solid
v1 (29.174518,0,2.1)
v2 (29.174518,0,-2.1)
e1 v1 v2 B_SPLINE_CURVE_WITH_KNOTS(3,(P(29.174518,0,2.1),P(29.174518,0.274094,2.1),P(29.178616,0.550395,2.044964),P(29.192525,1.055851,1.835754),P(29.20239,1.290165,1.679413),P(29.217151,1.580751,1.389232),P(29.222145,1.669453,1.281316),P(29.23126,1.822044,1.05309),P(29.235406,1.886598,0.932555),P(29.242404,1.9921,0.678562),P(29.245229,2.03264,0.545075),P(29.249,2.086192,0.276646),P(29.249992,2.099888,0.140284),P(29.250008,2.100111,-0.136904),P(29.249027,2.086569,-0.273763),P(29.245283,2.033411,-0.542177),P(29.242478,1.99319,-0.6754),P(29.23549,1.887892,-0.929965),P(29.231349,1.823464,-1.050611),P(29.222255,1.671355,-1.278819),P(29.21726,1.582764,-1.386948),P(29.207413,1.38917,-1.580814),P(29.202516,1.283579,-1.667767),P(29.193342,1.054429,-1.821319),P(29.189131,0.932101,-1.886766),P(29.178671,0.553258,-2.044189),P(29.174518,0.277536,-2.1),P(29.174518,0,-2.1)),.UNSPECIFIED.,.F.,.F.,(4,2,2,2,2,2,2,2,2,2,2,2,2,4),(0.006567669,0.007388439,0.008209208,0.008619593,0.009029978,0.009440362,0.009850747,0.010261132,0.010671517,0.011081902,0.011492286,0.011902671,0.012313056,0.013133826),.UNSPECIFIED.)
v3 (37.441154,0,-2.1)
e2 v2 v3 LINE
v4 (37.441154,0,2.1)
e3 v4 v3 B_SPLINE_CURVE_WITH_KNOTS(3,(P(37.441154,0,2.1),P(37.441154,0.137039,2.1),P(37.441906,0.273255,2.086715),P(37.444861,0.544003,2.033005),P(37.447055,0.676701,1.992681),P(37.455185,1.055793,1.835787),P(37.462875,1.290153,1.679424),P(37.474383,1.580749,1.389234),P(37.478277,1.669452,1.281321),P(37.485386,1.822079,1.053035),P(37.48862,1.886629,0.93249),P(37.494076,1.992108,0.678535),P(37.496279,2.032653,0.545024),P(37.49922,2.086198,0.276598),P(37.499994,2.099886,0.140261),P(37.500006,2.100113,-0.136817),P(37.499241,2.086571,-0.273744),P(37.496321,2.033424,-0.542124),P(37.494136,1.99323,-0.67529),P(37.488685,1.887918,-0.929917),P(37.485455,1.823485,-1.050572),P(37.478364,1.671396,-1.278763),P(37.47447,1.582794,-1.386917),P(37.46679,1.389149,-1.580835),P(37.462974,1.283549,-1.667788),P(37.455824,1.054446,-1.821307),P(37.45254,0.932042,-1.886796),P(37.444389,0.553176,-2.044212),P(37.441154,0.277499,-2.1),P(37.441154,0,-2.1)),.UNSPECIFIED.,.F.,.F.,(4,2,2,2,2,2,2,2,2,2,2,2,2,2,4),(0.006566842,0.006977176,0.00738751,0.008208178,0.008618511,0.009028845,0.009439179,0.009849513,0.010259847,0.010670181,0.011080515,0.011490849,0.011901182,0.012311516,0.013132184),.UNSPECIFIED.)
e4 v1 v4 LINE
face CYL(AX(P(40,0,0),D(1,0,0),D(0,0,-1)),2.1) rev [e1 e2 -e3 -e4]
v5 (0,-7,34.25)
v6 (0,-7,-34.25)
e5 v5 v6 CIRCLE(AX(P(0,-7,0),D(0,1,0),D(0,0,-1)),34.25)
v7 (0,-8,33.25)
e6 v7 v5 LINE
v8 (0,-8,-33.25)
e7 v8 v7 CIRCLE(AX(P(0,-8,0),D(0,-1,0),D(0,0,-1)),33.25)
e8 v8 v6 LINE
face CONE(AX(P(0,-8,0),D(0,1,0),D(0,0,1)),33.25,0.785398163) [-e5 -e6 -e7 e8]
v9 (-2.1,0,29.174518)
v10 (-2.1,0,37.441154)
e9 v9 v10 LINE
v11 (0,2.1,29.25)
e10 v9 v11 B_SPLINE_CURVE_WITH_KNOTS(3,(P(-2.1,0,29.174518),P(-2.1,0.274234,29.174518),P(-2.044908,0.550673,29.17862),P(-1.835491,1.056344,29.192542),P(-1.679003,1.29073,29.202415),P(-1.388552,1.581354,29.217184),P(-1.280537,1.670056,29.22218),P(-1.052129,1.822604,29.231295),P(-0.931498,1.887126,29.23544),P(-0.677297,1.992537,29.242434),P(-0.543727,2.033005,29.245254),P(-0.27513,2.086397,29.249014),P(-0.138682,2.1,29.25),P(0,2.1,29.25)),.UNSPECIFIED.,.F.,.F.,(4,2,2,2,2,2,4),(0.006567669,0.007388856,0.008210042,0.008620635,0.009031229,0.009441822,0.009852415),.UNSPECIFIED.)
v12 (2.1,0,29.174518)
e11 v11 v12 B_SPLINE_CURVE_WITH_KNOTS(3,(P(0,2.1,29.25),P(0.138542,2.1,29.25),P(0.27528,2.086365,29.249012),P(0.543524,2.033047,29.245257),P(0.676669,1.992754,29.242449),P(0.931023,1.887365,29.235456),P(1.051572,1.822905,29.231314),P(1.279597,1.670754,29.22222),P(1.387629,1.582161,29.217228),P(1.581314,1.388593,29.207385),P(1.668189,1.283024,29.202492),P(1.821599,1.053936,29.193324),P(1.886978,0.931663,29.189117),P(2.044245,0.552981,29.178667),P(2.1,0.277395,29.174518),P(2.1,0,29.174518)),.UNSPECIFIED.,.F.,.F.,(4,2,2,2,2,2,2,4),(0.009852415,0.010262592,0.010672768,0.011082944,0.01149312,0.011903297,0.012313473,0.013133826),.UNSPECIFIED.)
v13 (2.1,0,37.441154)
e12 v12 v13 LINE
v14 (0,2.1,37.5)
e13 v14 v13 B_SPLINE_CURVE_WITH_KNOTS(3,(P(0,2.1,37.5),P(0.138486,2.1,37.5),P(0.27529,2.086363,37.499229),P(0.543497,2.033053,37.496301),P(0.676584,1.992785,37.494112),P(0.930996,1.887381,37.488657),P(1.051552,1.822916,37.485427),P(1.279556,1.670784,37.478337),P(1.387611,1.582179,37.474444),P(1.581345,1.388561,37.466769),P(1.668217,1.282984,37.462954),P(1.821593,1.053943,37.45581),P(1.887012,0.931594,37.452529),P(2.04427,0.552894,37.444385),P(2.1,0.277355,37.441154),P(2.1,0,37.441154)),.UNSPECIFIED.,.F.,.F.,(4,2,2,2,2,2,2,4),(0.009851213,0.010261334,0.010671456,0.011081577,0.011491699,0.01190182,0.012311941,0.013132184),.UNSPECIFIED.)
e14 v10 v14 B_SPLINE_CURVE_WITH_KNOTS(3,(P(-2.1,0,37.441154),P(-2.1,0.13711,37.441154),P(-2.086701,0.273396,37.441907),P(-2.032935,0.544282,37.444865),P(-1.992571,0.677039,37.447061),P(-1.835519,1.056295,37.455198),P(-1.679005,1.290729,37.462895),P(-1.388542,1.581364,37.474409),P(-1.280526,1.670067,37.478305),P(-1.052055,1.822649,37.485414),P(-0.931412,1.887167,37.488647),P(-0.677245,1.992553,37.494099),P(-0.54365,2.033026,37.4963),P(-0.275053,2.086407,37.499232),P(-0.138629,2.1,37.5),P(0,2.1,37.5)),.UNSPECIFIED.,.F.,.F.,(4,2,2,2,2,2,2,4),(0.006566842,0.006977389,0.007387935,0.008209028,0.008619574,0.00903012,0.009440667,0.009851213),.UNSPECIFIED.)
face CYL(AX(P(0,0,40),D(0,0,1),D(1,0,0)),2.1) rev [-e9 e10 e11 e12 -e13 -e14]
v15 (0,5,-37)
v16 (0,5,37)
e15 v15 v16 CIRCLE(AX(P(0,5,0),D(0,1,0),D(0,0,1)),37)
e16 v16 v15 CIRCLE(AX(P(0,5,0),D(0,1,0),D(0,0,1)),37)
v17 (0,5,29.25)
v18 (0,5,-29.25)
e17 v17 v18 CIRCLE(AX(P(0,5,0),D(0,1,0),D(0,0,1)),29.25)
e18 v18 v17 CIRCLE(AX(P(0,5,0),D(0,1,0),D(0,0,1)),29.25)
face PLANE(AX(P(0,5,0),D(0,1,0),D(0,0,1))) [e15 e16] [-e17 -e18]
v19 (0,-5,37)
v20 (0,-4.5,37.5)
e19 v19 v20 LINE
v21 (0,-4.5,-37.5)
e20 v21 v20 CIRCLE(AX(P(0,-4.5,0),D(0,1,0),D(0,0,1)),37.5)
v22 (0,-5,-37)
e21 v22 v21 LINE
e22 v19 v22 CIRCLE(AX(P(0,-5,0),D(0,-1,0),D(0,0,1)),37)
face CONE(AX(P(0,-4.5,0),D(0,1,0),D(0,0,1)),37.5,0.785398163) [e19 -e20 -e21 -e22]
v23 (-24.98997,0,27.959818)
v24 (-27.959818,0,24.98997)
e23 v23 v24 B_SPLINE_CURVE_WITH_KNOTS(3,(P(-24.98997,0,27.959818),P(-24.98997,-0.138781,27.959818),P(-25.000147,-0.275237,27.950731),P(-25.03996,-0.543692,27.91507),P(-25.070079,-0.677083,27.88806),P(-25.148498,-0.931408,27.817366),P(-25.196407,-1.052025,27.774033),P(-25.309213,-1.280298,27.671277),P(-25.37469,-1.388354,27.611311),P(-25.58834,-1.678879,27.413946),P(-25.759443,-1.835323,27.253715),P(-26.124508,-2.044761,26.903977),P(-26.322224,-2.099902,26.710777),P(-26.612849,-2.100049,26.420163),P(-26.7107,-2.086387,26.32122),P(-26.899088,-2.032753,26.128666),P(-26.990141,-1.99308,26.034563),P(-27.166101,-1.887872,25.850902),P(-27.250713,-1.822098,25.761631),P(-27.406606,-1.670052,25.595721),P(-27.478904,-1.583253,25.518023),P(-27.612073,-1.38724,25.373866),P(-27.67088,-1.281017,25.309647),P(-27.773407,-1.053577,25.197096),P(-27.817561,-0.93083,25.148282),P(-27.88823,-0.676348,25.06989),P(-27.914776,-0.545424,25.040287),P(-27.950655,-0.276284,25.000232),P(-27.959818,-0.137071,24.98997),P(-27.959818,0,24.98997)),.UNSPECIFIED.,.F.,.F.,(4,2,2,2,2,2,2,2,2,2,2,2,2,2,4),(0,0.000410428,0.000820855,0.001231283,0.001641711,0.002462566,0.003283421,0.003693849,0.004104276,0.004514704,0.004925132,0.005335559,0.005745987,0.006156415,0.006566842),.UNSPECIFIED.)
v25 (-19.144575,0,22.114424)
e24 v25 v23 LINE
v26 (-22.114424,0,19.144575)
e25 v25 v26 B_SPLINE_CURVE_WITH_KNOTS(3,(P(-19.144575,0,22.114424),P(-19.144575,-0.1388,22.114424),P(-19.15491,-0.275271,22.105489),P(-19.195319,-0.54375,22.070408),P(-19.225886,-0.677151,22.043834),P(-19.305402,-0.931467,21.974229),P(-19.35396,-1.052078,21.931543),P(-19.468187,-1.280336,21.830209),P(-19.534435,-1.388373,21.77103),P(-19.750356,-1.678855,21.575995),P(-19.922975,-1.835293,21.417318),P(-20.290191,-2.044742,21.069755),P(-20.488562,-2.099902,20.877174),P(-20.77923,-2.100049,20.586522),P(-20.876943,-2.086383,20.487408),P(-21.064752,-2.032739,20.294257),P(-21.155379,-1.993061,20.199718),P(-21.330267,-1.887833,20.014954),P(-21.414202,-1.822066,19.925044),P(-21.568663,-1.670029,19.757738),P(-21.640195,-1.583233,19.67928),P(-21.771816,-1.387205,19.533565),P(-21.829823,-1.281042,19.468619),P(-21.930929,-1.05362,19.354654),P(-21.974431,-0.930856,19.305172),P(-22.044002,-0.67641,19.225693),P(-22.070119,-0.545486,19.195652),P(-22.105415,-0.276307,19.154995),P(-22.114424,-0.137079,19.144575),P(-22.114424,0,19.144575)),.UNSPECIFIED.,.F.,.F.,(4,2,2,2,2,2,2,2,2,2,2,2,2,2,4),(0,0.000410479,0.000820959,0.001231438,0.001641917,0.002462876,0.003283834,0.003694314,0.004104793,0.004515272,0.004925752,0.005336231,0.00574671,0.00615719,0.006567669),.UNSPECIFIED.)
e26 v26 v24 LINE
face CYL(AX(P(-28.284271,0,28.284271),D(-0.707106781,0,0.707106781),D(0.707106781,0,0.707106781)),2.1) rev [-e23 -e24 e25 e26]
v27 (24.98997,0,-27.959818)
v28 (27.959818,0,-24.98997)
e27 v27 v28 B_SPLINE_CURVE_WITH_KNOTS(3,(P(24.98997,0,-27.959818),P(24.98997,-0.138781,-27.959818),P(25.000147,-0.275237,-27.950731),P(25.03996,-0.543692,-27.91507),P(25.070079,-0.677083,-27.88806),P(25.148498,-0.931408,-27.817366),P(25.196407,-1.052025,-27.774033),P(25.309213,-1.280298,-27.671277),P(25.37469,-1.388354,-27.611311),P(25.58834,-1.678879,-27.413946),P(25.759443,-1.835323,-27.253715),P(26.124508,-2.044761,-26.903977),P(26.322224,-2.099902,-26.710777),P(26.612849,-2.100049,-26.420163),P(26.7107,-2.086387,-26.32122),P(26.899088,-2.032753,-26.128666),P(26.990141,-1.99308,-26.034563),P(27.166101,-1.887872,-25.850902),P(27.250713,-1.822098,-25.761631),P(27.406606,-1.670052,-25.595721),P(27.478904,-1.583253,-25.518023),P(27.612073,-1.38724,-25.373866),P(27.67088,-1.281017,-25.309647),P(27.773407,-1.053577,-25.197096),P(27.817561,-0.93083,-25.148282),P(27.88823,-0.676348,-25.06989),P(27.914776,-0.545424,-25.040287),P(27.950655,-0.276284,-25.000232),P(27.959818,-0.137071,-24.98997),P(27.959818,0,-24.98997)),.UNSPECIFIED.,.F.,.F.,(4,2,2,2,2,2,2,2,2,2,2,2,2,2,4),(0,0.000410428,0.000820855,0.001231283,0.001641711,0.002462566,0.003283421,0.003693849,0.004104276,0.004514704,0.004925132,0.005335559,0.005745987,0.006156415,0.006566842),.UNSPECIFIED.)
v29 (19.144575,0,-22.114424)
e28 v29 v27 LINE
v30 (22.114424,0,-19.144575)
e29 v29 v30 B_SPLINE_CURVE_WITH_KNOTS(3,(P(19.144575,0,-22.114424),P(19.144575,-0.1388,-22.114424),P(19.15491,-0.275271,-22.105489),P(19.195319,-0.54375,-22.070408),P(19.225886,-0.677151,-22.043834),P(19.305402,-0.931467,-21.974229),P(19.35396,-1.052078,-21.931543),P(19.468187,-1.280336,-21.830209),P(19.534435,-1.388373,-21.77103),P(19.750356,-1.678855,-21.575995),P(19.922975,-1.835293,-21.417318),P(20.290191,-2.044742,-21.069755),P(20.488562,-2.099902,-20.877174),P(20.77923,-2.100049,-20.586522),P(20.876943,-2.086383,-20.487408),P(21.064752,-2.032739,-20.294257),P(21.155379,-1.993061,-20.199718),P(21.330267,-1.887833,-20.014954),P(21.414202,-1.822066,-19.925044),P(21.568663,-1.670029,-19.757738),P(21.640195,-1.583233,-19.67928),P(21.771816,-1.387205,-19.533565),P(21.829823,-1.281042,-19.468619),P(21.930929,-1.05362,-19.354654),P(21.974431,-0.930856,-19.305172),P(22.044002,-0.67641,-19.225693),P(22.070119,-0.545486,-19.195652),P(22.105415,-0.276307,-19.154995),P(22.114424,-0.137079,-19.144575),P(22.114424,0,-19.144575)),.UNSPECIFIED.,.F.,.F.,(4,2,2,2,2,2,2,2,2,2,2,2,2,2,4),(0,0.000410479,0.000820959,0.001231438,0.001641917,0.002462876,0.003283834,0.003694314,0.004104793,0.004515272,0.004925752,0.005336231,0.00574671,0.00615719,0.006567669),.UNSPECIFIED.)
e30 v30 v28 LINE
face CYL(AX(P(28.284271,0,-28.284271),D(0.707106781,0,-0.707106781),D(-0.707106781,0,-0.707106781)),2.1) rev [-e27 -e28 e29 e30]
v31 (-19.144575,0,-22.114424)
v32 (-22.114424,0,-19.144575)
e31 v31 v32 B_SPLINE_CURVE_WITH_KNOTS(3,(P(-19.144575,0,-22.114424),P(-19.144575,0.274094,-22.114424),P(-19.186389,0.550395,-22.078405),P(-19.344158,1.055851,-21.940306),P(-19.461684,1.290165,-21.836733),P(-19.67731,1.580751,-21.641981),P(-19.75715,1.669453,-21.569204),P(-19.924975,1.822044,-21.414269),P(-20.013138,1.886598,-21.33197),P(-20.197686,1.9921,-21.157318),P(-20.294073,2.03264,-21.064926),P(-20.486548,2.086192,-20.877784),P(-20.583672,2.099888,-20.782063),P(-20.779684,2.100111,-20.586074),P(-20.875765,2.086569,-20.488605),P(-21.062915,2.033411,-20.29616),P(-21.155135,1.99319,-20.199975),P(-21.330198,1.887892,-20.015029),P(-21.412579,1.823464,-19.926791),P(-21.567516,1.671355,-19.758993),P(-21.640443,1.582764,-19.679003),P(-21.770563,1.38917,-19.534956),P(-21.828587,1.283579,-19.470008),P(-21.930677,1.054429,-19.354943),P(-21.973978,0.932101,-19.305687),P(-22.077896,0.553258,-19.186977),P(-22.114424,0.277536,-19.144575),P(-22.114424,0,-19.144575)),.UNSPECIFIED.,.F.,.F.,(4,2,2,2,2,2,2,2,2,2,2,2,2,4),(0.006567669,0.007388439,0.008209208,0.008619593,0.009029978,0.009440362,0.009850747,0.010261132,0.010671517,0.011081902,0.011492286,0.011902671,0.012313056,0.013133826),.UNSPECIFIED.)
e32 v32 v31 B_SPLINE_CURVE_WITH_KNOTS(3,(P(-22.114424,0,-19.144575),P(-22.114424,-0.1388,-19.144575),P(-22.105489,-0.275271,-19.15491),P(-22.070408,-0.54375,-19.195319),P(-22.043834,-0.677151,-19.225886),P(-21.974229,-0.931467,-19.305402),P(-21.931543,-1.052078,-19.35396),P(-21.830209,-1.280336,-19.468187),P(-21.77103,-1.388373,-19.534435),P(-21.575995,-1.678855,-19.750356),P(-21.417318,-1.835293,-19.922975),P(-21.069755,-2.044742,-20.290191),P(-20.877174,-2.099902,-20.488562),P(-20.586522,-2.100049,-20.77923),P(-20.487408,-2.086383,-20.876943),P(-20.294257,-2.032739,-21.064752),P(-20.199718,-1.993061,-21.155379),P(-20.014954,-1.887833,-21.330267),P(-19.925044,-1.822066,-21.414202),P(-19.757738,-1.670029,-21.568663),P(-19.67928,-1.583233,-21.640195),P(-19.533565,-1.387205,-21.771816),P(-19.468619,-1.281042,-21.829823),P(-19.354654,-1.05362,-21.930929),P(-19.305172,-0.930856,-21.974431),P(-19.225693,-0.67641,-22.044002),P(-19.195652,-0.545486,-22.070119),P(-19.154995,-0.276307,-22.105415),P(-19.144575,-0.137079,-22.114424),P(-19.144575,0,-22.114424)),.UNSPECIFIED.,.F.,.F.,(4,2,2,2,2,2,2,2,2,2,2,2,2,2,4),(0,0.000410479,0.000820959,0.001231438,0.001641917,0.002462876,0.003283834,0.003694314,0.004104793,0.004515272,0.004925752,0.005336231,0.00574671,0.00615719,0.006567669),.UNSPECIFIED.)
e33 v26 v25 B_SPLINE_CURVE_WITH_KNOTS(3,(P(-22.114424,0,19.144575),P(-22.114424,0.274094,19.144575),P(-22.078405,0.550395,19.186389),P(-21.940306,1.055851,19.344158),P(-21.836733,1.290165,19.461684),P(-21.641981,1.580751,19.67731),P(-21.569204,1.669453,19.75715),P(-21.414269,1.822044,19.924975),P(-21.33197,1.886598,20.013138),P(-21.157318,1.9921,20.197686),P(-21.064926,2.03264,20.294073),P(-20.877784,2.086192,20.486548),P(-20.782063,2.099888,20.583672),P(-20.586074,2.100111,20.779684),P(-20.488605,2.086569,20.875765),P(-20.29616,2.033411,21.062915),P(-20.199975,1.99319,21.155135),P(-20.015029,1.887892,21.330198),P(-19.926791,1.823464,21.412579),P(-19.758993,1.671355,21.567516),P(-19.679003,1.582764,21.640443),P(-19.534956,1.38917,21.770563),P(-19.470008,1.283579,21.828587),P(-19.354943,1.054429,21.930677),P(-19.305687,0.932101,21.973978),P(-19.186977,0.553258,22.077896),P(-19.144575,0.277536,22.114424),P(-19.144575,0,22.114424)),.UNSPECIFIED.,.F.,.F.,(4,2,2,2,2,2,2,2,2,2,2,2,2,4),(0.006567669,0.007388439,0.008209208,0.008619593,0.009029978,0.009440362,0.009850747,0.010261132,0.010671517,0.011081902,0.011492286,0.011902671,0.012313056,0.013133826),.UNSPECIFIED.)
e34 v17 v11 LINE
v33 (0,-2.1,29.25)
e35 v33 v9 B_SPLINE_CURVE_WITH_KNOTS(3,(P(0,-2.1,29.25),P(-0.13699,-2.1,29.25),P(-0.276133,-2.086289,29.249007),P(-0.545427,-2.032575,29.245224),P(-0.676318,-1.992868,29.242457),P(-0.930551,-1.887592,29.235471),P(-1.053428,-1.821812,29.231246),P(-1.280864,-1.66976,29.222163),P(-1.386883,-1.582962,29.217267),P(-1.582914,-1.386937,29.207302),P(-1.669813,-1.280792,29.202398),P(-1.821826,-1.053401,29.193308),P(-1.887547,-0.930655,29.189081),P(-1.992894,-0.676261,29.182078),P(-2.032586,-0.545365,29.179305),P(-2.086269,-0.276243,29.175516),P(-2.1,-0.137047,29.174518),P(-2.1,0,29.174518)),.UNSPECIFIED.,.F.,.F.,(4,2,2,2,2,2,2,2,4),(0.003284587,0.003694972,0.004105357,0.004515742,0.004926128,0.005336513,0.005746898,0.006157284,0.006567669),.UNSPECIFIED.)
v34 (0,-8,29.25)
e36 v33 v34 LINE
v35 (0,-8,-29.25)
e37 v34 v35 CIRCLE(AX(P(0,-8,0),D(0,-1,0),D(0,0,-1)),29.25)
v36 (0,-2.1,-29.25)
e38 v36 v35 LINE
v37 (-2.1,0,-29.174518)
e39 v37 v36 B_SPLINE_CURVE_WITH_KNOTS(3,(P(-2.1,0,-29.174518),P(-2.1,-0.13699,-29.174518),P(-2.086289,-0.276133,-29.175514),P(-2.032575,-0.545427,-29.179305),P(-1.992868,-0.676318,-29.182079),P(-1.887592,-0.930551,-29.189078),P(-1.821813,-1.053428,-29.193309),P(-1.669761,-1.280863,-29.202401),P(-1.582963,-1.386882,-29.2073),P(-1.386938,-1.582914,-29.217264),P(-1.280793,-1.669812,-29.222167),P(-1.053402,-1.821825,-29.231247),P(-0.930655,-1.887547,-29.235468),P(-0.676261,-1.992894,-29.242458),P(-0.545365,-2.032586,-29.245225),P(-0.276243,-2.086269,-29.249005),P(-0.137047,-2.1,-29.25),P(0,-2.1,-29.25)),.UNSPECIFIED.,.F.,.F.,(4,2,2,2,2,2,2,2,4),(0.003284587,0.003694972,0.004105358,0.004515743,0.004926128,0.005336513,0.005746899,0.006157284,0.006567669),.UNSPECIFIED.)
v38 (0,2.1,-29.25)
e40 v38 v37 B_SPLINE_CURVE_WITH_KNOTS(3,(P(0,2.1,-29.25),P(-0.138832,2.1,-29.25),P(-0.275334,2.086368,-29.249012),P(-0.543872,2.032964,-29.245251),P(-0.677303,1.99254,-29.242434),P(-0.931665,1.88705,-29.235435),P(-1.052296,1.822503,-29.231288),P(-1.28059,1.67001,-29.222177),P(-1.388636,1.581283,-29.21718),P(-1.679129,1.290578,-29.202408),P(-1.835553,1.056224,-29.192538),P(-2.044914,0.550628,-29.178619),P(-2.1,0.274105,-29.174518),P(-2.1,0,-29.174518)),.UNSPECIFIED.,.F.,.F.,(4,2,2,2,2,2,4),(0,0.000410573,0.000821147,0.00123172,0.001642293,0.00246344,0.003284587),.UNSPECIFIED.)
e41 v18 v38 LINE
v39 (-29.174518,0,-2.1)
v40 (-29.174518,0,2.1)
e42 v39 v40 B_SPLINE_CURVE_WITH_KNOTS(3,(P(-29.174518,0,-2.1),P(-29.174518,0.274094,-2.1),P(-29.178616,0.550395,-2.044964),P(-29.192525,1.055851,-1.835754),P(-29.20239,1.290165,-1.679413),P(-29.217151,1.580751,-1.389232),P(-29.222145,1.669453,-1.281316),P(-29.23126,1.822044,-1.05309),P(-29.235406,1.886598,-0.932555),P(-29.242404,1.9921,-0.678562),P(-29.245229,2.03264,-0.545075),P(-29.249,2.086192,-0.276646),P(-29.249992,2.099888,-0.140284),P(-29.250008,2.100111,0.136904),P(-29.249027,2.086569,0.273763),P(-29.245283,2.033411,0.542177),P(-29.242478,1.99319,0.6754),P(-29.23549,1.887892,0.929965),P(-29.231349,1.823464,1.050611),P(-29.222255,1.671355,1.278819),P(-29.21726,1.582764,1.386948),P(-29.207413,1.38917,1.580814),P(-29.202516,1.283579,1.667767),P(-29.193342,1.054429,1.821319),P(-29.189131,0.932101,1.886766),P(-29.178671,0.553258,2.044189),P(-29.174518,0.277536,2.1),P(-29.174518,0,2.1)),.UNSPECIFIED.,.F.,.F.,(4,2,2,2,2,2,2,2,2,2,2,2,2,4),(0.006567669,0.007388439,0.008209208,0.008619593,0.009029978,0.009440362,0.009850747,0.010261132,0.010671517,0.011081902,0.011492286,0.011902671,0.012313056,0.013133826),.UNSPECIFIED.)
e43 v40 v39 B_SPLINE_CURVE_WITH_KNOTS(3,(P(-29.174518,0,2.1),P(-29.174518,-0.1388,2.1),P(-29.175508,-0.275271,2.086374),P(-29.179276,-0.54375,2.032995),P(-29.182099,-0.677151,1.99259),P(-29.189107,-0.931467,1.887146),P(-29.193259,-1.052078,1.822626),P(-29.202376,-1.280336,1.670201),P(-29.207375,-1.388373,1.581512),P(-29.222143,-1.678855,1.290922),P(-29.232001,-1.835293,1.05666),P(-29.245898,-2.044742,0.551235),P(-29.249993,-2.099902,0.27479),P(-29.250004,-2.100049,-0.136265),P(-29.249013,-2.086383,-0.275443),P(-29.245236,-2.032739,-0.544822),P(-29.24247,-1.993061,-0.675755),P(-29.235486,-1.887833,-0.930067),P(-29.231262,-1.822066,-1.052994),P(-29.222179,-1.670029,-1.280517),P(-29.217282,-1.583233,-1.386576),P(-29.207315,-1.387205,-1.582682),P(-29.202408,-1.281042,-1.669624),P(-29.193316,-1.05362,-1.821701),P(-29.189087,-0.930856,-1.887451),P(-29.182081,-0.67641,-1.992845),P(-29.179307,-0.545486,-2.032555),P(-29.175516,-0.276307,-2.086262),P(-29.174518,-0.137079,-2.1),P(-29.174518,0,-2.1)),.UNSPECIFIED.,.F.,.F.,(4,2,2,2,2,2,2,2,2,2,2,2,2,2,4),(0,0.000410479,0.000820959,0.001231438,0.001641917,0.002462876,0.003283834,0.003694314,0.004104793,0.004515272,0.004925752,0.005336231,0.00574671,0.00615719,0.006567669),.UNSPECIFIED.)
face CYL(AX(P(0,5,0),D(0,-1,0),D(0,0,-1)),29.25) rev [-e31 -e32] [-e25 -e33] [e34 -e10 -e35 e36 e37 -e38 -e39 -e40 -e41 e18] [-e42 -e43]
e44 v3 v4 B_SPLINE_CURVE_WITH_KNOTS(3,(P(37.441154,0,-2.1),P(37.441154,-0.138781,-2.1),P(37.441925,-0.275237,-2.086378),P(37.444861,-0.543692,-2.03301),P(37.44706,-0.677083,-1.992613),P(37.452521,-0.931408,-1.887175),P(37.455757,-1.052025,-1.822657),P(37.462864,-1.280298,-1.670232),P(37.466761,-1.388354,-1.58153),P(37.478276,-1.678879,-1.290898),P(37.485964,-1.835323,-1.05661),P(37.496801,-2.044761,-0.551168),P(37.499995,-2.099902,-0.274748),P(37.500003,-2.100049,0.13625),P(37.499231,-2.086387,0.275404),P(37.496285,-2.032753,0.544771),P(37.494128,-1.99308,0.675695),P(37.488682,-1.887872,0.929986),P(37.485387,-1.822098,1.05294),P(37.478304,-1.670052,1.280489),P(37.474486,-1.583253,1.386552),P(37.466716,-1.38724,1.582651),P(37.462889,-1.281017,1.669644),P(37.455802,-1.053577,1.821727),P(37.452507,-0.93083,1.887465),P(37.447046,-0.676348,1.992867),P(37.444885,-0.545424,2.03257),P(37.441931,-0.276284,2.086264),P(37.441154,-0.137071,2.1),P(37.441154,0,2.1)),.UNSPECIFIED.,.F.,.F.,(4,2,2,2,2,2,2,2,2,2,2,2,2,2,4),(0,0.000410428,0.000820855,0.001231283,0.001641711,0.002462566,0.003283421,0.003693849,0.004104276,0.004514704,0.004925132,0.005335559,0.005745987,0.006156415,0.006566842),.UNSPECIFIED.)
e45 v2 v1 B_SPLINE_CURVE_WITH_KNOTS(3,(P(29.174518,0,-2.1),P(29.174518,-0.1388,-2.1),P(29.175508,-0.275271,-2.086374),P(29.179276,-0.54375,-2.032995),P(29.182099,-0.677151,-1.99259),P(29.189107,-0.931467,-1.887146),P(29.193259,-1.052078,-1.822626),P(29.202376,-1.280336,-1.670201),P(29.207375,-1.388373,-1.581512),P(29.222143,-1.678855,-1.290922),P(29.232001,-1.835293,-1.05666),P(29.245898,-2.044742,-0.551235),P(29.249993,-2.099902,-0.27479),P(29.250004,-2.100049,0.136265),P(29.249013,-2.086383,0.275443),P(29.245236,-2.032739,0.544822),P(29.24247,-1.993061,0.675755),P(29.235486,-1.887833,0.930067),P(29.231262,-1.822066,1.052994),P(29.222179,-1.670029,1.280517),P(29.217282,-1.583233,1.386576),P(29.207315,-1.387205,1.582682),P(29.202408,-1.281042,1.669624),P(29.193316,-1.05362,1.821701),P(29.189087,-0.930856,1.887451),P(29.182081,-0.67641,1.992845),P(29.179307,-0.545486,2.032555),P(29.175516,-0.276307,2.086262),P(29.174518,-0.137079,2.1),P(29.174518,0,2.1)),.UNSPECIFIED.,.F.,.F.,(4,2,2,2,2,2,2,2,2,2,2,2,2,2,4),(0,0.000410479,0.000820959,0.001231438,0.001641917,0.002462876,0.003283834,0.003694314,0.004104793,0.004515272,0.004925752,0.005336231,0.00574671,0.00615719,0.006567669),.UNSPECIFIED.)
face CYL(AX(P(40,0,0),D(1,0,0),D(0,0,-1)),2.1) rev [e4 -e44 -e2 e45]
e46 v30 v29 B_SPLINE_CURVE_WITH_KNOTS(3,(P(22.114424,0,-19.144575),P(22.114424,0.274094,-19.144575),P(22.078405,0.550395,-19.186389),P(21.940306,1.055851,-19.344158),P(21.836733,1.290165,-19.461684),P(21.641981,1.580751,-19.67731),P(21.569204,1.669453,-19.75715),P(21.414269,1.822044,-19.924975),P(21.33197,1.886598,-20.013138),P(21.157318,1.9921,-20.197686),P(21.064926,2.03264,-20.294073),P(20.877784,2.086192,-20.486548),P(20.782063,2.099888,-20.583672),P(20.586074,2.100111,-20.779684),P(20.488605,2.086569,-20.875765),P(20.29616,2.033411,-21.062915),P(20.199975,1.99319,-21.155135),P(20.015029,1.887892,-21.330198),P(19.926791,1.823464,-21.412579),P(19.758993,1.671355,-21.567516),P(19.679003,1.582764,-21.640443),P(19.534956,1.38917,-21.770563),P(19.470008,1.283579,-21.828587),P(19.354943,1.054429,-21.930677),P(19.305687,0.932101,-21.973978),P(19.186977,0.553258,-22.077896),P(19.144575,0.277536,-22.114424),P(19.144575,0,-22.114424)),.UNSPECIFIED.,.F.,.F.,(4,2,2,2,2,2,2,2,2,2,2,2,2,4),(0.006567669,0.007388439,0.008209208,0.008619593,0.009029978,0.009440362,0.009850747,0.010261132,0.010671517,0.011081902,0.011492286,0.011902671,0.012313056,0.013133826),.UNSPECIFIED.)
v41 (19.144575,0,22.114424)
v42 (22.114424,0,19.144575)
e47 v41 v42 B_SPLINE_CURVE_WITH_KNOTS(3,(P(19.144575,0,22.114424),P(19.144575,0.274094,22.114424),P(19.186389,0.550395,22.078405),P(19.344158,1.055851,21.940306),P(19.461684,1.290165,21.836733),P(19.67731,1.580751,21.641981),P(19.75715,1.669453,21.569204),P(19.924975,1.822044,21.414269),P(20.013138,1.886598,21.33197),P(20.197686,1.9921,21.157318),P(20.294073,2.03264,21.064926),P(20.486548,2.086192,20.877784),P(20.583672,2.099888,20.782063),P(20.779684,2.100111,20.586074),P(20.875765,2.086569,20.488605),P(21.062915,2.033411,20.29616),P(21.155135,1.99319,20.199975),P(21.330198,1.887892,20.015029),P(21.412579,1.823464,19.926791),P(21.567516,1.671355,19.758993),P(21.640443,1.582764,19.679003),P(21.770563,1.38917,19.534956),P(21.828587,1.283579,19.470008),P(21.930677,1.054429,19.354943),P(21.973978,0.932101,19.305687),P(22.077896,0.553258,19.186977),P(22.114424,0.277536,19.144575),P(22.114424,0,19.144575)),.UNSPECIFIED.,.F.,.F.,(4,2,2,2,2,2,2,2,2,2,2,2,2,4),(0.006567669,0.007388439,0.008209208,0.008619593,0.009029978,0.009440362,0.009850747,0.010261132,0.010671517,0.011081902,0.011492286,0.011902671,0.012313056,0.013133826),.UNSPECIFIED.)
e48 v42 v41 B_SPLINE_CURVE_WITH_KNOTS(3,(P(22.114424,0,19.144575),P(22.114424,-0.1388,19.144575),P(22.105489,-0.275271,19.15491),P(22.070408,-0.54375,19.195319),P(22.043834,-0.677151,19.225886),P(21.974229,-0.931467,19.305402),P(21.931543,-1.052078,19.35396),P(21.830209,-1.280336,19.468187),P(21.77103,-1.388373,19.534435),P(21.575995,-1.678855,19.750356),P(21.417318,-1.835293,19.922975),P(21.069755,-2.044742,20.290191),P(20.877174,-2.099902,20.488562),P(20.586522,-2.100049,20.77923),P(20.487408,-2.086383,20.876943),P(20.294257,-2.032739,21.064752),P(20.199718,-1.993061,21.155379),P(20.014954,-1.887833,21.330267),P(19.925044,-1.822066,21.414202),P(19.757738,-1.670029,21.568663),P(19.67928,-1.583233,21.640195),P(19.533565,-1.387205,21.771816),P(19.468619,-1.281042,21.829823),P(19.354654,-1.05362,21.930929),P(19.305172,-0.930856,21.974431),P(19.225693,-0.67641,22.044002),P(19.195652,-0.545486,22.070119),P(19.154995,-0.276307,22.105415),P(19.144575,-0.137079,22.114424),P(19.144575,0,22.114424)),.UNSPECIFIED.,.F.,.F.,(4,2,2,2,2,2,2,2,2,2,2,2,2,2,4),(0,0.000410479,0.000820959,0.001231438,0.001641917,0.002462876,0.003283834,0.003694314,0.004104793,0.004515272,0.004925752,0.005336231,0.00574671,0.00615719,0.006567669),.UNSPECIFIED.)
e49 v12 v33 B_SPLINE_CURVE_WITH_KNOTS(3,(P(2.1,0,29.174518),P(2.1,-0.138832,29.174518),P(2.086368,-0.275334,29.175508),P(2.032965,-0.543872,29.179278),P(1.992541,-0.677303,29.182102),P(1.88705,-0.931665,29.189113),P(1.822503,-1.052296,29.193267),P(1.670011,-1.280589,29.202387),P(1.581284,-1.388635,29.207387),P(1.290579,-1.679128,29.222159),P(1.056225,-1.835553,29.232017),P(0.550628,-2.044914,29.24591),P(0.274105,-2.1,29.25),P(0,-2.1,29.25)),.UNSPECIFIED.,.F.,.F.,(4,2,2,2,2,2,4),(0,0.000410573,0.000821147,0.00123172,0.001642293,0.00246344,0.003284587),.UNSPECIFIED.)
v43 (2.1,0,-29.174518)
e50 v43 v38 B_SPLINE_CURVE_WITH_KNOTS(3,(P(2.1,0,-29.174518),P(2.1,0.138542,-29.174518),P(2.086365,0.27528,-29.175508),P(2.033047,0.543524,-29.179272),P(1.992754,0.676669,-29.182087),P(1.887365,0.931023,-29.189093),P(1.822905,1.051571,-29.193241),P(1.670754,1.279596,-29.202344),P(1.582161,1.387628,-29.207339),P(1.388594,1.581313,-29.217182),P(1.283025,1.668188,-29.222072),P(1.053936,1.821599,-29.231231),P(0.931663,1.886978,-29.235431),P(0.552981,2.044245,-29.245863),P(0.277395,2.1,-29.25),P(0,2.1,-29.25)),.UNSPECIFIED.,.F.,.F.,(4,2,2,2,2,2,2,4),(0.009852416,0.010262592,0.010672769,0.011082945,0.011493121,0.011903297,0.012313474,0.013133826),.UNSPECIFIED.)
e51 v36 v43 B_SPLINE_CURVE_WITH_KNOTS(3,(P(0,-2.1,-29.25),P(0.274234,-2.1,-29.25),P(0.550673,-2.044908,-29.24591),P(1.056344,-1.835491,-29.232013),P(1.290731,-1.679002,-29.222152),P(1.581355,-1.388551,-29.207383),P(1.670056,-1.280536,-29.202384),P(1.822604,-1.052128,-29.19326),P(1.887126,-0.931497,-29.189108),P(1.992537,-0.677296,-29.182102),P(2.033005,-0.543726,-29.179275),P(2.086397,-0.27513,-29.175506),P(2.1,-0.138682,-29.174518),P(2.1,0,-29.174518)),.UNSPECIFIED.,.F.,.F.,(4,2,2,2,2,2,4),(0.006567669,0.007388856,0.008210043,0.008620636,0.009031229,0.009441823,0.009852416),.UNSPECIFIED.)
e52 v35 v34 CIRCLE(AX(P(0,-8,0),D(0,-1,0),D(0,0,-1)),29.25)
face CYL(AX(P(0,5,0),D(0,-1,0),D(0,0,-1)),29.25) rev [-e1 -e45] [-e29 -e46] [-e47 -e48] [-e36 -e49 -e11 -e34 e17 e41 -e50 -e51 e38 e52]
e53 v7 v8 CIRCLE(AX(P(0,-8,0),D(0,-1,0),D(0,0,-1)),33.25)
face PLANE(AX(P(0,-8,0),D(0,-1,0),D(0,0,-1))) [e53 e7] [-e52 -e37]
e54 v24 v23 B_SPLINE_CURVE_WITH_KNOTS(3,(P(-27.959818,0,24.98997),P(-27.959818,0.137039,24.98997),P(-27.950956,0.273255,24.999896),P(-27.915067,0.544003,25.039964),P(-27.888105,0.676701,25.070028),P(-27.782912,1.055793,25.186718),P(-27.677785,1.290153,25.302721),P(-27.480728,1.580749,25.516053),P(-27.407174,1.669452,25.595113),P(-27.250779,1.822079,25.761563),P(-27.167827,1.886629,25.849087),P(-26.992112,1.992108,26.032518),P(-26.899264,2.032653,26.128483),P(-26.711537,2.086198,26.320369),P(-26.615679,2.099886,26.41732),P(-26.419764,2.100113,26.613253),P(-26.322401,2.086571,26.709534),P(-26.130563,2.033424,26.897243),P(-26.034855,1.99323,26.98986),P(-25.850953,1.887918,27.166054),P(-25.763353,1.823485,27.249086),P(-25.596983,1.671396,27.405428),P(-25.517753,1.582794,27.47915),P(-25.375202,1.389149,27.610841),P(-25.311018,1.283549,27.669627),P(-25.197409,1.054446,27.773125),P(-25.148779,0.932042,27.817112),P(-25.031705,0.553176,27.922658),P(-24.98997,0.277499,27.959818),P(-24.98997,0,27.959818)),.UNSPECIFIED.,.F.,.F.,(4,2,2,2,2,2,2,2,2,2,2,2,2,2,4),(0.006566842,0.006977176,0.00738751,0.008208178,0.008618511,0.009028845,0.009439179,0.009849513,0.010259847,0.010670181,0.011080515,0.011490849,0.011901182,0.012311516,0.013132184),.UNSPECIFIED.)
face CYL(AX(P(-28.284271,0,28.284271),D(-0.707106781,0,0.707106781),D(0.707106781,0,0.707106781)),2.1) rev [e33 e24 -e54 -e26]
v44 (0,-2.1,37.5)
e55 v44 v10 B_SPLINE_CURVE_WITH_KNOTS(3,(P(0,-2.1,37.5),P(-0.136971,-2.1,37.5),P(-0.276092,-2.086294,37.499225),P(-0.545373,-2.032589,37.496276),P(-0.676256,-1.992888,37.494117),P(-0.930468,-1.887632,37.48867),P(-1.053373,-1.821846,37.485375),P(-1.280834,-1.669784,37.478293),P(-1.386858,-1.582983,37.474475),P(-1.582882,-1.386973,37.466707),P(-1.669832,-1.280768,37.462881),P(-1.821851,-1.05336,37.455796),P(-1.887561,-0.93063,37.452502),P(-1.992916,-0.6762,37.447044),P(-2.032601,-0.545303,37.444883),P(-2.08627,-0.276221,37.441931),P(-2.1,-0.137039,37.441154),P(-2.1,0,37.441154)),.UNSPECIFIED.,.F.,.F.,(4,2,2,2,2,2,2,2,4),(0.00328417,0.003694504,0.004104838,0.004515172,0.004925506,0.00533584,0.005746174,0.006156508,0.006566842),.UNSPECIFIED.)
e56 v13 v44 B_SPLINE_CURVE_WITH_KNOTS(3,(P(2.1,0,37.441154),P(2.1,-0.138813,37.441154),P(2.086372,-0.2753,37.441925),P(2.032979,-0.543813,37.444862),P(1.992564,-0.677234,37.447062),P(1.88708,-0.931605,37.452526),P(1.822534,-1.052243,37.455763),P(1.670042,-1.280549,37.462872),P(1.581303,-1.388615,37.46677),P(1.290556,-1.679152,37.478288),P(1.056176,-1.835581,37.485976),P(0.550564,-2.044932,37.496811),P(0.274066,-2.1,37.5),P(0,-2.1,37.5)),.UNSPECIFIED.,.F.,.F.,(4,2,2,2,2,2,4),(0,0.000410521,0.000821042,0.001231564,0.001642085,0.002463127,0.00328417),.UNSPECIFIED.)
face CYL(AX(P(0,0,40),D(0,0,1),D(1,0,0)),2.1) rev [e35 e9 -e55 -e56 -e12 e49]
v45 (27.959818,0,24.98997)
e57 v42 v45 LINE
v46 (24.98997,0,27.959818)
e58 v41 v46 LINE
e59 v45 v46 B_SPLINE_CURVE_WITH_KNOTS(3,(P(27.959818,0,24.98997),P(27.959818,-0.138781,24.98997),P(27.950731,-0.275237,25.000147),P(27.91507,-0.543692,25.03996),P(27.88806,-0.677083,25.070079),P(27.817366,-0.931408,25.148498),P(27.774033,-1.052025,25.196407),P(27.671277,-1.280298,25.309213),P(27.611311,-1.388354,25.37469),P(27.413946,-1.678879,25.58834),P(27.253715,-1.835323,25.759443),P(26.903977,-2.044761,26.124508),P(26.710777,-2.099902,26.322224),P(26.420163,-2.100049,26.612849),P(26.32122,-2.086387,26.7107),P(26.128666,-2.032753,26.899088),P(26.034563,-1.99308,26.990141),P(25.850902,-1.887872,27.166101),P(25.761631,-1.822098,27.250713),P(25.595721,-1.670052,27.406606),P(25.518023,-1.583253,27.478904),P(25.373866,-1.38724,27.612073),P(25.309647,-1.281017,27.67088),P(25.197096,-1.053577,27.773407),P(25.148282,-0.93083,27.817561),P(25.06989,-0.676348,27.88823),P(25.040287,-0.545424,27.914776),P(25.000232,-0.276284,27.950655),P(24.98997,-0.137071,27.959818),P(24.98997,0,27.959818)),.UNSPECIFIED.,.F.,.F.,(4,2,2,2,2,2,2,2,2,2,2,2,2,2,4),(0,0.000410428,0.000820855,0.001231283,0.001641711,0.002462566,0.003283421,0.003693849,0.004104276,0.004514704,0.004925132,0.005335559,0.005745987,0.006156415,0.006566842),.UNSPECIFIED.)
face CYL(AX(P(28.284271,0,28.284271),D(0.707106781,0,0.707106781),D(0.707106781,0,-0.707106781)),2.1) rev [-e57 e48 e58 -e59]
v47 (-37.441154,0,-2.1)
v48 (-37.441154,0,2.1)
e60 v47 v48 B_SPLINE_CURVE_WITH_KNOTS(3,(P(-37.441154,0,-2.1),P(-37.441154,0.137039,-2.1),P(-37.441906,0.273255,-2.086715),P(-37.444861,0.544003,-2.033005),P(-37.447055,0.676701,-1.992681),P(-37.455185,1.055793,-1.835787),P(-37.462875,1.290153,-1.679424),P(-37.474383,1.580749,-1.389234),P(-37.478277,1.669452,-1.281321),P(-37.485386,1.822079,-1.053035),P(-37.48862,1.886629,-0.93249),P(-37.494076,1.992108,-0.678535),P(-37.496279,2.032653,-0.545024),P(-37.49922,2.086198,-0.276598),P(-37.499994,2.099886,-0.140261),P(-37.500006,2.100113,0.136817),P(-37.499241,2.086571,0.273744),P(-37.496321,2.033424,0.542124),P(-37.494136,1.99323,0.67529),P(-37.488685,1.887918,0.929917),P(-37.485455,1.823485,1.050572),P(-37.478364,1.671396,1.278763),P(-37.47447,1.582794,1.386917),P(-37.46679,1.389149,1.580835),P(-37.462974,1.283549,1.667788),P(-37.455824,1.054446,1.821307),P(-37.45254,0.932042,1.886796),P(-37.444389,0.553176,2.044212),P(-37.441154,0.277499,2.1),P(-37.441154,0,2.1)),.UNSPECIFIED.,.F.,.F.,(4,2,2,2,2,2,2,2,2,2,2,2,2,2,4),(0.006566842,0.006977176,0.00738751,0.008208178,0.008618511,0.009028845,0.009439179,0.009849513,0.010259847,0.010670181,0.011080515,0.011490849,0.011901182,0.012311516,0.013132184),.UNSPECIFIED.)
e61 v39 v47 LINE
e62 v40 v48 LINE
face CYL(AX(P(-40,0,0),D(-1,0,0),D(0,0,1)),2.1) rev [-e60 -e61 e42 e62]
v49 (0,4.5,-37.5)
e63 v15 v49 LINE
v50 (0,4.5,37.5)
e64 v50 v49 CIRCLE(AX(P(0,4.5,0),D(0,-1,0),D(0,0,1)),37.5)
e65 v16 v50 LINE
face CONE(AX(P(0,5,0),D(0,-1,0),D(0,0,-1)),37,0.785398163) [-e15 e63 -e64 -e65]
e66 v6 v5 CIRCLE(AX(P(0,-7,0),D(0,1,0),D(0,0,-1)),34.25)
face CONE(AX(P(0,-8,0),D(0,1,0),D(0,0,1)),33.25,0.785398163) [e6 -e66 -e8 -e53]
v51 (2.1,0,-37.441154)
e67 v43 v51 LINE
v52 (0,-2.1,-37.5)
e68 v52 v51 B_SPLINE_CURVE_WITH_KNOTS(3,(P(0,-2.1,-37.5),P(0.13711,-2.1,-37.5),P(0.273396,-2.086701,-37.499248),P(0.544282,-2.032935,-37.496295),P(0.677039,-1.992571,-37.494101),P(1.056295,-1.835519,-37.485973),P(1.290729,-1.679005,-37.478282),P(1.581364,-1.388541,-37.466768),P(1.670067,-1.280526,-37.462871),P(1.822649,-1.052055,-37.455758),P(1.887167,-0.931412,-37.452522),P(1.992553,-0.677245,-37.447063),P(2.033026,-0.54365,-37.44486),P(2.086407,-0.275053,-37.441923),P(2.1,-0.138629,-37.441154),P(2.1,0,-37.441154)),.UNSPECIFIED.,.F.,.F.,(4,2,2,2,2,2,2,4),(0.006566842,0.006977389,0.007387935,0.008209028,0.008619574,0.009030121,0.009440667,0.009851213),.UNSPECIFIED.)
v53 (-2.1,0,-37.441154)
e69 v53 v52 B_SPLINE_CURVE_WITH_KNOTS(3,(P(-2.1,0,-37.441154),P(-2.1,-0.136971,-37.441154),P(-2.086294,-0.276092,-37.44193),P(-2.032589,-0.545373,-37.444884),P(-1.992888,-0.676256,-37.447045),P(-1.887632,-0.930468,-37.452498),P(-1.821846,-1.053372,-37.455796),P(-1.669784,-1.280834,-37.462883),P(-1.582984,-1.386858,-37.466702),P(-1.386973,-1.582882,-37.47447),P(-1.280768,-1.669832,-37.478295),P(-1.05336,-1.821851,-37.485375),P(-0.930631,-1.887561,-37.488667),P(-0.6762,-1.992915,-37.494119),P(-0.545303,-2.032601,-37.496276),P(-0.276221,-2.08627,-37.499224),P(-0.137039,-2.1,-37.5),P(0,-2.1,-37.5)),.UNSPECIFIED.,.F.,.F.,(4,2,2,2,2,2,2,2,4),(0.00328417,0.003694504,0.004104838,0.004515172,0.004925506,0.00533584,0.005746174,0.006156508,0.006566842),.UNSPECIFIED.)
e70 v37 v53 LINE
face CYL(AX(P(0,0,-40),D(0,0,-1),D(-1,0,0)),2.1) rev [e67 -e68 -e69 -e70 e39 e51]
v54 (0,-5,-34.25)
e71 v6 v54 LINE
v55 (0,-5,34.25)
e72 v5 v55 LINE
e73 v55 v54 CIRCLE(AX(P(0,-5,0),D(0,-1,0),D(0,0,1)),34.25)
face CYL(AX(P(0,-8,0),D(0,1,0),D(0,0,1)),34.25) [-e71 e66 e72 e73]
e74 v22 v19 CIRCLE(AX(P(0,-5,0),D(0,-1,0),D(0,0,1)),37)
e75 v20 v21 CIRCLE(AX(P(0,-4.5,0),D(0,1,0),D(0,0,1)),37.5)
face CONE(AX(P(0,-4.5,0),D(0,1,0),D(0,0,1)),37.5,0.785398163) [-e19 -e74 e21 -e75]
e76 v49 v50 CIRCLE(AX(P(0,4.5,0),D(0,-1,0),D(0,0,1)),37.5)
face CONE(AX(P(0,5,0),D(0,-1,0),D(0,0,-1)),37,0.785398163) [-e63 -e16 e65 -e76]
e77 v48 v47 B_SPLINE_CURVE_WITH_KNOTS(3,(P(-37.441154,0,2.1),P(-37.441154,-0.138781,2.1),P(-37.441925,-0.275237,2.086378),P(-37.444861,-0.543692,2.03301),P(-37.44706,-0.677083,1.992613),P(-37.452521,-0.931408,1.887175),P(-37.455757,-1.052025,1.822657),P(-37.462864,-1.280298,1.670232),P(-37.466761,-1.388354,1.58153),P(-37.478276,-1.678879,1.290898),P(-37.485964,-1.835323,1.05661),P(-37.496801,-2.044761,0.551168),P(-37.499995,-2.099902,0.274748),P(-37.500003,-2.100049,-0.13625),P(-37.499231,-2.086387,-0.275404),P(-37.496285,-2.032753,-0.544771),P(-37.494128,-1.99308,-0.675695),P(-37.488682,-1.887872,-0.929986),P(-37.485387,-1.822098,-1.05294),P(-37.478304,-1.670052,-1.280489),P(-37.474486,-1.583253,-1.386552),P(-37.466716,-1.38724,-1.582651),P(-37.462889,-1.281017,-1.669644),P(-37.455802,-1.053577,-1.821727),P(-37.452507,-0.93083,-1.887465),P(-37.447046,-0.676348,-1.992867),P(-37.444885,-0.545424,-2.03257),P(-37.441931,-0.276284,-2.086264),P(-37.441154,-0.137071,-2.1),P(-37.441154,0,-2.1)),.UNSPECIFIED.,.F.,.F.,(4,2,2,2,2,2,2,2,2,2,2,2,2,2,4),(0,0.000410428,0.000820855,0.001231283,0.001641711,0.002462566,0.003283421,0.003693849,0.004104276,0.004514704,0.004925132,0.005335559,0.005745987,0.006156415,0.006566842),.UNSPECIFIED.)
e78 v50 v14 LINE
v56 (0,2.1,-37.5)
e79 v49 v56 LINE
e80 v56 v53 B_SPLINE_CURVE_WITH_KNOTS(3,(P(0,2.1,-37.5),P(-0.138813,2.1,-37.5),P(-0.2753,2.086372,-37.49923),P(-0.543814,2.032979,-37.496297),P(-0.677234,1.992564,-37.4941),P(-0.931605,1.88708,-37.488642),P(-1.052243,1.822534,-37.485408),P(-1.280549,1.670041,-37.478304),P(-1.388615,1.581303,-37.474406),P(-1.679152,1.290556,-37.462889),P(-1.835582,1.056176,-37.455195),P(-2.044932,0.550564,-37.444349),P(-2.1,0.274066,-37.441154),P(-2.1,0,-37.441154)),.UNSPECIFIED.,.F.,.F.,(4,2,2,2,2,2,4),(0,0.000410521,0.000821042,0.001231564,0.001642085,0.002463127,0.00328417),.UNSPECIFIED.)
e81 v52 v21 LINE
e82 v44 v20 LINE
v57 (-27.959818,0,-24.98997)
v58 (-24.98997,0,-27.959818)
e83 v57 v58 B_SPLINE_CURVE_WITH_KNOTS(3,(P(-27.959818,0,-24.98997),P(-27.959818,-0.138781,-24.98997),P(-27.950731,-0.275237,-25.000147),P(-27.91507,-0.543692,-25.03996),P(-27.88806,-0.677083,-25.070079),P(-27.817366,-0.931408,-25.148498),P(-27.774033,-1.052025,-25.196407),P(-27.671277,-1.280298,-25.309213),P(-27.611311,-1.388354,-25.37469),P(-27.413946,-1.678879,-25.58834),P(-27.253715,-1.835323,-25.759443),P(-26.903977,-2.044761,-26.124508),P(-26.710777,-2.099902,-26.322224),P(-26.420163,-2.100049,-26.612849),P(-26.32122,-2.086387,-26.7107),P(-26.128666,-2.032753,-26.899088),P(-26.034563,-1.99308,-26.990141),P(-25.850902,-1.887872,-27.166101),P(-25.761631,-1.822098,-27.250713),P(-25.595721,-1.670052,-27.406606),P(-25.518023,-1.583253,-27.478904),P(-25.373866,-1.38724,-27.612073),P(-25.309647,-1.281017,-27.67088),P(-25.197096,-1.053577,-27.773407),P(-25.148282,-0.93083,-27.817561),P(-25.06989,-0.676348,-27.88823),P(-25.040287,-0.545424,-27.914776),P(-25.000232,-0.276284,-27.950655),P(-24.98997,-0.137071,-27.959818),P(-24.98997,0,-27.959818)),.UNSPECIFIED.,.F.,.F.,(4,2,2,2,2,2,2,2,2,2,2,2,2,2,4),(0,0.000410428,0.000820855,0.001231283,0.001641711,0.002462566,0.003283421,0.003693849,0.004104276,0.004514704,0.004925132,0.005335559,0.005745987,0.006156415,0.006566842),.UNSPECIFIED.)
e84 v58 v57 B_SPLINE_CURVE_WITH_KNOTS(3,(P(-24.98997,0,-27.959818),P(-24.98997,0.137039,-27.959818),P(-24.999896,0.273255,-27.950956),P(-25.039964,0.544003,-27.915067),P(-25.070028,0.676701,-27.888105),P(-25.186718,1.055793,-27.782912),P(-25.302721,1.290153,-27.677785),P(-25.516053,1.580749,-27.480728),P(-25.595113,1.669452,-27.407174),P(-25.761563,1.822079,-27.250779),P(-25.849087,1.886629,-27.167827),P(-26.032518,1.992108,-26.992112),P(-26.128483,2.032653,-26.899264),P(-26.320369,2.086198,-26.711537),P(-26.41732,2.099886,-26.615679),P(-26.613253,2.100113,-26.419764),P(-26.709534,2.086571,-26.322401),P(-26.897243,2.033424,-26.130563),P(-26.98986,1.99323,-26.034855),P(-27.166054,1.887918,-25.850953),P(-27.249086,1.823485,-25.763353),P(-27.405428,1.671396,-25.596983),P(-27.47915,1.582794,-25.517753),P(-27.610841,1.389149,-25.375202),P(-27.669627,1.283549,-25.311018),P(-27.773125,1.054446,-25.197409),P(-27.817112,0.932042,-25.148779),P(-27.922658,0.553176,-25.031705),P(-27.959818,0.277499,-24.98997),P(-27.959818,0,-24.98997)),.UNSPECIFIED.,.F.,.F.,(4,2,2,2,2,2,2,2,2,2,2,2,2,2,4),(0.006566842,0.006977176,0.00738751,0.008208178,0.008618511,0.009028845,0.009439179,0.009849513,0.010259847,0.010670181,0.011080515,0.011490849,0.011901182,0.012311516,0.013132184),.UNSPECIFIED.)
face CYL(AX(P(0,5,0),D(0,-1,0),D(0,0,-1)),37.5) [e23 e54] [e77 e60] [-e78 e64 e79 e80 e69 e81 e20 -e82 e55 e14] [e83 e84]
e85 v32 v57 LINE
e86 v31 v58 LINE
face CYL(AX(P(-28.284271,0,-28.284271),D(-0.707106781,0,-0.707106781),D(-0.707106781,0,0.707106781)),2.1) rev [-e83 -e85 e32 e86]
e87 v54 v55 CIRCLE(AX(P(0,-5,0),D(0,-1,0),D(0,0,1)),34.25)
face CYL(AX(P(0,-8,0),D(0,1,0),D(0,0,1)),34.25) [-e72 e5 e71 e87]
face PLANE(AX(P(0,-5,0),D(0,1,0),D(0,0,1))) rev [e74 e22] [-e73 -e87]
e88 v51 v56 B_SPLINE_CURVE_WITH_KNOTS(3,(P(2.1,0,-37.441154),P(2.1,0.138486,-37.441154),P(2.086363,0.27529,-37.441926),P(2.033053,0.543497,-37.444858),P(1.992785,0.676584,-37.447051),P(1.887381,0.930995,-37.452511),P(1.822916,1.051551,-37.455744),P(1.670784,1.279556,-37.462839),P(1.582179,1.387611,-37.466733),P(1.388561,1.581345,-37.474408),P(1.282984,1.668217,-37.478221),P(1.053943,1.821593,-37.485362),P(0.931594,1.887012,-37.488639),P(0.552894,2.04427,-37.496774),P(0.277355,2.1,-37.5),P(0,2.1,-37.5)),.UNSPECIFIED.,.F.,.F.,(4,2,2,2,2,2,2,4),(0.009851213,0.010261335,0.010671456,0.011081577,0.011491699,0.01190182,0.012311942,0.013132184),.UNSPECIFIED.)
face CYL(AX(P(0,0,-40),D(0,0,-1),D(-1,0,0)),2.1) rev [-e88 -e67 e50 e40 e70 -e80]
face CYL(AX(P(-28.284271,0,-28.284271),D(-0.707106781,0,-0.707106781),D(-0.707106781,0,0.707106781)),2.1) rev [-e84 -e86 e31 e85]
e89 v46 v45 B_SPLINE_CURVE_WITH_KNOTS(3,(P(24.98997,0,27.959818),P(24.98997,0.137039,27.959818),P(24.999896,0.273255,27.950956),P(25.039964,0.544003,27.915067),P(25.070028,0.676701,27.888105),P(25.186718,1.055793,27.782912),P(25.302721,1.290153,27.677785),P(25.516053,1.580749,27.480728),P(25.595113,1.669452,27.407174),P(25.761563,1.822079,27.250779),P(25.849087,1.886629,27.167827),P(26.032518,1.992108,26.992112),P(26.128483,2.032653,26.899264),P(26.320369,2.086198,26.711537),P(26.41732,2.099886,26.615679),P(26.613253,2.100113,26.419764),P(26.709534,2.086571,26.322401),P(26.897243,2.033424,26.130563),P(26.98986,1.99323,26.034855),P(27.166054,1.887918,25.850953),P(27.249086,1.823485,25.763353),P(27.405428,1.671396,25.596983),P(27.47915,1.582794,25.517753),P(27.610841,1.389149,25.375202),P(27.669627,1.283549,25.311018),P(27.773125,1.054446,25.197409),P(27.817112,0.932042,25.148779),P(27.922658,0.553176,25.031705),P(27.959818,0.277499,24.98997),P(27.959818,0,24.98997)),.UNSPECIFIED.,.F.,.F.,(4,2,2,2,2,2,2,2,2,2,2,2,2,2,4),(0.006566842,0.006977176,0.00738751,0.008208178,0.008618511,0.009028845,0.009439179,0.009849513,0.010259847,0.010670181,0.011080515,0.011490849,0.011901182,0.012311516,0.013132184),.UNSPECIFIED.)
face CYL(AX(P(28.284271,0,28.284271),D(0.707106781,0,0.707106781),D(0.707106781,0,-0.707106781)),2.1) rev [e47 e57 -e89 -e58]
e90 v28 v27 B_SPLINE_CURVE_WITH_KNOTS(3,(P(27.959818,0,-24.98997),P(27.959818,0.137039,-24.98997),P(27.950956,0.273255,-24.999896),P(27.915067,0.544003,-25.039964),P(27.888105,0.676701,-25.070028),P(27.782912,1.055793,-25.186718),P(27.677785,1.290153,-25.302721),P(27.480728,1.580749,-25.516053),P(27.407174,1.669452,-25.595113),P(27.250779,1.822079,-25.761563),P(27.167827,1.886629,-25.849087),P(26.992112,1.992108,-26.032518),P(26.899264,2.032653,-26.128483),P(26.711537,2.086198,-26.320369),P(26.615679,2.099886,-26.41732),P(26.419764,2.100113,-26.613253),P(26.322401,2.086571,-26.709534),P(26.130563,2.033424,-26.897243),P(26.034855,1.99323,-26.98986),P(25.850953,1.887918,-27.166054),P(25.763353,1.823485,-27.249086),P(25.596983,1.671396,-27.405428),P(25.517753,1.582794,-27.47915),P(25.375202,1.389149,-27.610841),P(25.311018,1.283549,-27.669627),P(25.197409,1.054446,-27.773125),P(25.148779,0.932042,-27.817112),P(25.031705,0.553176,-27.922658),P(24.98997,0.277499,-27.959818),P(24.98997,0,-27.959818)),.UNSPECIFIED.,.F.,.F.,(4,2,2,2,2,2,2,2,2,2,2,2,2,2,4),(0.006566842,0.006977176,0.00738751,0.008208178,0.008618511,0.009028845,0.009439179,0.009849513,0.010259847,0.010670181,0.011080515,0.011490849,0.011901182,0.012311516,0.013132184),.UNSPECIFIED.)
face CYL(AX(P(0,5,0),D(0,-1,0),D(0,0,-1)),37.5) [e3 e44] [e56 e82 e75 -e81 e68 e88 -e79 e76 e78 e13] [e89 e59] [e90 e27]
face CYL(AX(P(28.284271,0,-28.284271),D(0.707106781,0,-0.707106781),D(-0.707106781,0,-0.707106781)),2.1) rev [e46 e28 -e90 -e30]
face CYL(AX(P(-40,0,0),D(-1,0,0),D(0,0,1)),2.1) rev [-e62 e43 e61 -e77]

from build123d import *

# Parameters (mm, degrees)
SKETCH_1_R               = 37.5
SKETCH_1_R_2             = 29.25
EXTRUDE_1_DEPTH          = 5
PATTERN_CIRCULAR_1_COUNT = 8
CHAMFER_1_SIZE           = 0.5
EXTRUDE_START            = 3
SKETCH_6_R               = 34.25
SKETCH_6_R_2             = 29.25
EXTRUDE_2_DEPTH          = 3
CHAMFER_2_SIZE           = 1


with BuildPart() as part:
    # 草图1 → 凸台-拉伸1 (new, symmetric)
    with BuildSketch(Plane(origin=(0, 0, 0), x_dir=(1, 0, 0), z_dir=(0, 1, 0))):
        with Locations(Location((0, 0, 0), (0, 0, 270))):
            Circle(SKETCH_1_R)
        with Locations(Location((0, 0, 0), (0, 0, 270))):
            Circle(SKETCH_1_R_2, mode=Mode.SUBTRACT)
    extrude(amount=EXTRUDE_1_DEPTH, both=True)

    # 草图2 → Ø4.2 (4.2) 直径孔1 (revolve, cut)
    with BuildSketch(Plane(origin=(0, 0, 40), x_dir=(0, -1, 0), z_dir=(1, 0, 0))):
        Polygon((0, 0), (0, 16.2618073), (2.1, 15), (2.1, 0), align=None)
    hole_wizard_4_2_4_2_1 = revolve(axis=Axis((0, 0, 46.35), (0, 0, -1)), mode=Mode.SUBTRACT)

    # 阵列(圆周)1: Ø4.2 (4.2) 直径孔1 ×8 about axis
    pattern_circular_1_axis = Axis((0, 5, 0), (0, -1, 0))
    for i in range(1, PATTERN_CIRCULAR_1_COUNT):
        add(hole_wizard_4_2_4_2_1.rotate(pattern_circular_1_axis, i * 360 / PATTERN_CIRCULAR_1_COUNT), mode=Mode.SUBTRACT)

    # 倒角1
    chamfer_1_edges = [part.edges().sort_by_distance(p)[0] for p in [
        (0, -5, -37.5),
        (0, 5, -37.5),
    ]]
    chamfer(chamfer_1_edges, length=CHAMFER_1_SIZE)

    # 草图6 → 凸台-拉伸2 (add)
    with BuildSketch(Plane.XZ.offset(5).offset(EXTRUDE_START)):
        with Locations(Location((0, 0, 0), (0, 0, 90))):
            Circle(SKETCH_6_R)
        with Locations(Location((0, 0, 0), (0, 0, 270))):
            Circle(SKETCH_6_R_2, mode=Mode.SUBTRACT)
    extrude(amount=-EXTRUDE_2_DEPTH)

    # 倒角2
    chamfer_2_edges = [part.edges().sort_by_distance(p)[0] for p in [
        (0, -8, -34.25),
    ]]
    chamfer(chamfer_2_edges, length=CHAMFER_2_SIZE)


solid = part.part
